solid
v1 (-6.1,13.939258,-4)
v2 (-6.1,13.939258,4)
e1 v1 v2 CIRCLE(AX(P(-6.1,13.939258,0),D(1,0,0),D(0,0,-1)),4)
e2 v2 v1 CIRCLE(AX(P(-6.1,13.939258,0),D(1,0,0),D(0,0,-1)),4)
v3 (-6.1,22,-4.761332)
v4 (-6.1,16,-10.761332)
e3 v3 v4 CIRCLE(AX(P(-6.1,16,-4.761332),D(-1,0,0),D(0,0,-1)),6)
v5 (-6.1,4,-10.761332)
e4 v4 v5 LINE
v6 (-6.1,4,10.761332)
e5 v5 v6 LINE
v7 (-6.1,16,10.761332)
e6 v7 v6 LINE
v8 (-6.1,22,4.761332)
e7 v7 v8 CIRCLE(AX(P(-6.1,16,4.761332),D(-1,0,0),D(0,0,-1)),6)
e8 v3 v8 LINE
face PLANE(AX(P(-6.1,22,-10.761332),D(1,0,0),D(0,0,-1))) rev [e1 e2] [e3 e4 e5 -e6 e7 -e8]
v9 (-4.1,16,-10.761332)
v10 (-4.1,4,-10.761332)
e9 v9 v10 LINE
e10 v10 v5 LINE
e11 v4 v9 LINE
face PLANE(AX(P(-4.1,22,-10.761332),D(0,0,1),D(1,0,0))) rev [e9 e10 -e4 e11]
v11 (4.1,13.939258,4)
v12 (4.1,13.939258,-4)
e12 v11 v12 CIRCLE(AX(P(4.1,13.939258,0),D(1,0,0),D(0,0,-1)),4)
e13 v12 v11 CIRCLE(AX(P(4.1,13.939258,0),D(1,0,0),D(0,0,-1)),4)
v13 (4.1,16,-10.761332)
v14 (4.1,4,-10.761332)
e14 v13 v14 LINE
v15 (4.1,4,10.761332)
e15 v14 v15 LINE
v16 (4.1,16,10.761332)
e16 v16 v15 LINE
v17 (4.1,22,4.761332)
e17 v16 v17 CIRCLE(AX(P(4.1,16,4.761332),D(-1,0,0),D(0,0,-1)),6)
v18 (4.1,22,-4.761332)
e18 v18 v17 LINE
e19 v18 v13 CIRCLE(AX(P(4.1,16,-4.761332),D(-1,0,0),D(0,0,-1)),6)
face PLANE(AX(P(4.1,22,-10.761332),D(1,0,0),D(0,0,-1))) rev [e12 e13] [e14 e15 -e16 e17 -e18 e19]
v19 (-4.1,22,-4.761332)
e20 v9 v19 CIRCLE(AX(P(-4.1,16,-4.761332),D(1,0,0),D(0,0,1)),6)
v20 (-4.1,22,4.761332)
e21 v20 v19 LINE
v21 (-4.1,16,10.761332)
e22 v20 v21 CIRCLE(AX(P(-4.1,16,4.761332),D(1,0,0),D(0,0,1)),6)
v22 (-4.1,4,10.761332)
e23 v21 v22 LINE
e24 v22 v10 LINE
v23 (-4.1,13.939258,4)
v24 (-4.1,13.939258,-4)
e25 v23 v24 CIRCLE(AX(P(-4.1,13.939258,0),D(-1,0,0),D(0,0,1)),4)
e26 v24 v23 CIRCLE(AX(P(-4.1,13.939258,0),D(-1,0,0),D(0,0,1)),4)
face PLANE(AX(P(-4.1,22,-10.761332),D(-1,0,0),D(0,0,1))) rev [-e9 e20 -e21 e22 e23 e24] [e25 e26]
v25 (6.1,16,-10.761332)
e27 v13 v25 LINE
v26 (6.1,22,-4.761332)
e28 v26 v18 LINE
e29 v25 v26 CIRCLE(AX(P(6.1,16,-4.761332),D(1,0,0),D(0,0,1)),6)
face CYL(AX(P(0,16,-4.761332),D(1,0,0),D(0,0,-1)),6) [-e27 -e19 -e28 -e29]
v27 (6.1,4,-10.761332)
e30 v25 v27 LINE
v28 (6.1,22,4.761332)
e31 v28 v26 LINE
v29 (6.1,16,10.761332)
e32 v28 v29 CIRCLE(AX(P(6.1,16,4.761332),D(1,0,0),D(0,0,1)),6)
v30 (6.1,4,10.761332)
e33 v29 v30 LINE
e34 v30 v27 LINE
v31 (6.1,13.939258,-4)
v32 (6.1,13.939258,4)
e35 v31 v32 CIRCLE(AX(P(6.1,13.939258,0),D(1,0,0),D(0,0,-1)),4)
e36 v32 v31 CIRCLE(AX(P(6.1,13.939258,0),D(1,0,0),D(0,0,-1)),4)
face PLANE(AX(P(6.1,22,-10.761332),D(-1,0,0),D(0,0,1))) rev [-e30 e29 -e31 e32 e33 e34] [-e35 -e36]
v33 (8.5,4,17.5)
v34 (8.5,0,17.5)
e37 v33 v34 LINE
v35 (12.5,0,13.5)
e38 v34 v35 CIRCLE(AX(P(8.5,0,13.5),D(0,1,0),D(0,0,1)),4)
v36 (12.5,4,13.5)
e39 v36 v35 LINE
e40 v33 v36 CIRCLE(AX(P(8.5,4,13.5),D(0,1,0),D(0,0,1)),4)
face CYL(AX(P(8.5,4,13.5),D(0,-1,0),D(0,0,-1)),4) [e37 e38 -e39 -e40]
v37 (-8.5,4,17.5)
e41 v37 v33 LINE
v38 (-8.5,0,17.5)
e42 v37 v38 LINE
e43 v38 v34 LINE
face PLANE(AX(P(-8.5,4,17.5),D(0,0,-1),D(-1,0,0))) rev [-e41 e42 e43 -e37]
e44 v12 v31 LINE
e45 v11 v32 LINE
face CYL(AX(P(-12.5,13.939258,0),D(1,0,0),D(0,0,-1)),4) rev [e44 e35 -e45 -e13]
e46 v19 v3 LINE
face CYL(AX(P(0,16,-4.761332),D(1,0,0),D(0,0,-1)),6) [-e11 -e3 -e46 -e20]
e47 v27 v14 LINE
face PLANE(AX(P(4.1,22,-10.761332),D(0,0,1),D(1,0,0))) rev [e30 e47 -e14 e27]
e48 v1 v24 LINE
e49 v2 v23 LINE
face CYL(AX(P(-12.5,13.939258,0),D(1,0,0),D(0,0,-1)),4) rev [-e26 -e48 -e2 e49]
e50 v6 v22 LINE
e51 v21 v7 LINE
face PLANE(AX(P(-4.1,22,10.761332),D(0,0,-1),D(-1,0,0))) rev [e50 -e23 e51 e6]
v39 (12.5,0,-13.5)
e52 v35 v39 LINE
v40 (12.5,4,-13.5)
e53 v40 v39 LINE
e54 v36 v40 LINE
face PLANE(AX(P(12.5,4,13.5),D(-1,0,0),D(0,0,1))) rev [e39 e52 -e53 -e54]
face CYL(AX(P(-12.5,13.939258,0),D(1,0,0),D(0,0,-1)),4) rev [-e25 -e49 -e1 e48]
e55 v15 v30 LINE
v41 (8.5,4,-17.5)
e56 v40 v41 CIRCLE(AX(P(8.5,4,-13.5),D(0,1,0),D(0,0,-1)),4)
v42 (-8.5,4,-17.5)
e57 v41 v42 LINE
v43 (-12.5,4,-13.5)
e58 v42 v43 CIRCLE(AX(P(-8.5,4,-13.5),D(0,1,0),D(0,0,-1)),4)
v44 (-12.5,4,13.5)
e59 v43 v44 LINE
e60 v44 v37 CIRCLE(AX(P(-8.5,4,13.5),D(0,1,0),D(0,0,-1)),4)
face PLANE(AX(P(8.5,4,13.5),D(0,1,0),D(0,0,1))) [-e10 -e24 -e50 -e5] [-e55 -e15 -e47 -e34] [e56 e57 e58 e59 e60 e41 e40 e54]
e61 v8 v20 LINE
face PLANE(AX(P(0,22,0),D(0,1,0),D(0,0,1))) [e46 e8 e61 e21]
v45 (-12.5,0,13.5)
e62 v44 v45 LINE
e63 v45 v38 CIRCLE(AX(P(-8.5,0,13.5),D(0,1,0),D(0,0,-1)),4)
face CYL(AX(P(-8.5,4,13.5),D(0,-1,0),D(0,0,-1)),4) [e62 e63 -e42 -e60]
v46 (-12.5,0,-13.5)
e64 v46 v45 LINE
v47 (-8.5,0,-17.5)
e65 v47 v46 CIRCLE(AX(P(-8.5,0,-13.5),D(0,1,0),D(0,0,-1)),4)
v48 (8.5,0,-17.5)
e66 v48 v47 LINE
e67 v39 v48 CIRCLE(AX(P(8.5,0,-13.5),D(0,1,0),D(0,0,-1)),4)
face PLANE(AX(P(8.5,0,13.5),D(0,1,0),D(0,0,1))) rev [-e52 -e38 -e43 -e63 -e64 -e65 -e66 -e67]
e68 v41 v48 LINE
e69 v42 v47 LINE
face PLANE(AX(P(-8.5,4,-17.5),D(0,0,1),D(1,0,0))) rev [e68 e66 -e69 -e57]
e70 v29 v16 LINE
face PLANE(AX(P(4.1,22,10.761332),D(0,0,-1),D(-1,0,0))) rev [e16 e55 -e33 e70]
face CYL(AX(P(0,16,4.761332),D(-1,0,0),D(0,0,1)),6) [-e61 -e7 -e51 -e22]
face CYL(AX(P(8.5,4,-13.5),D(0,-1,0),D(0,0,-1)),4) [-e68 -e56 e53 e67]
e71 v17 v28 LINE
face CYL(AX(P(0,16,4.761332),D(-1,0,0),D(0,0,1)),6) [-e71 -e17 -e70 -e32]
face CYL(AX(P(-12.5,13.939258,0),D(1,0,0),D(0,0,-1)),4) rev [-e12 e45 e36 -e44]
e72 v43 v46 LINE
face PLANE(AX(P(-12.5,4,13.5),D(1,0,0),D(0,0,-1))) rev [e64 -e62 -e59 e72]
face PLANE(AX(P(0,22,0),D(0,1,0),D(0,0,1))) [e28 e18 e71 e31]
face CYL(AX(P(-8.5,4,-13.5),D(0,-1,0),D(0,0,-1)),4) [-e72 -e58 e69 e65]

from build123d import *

# Parameters (mm, degrees)
BOSS_EXTRU_1_DEPTH = 4
SKETCH2_W          = 2
SKETCH2_H          = 21.522663516
BOSS_EXTRU_2_DEPTH = 18
FILLET1_R          = 6
SKETCH3_R          = 4
CUT_EXTRUDE1_DEPTH = 34.707714251


with BuildPart() as part:
    # Sketch1 → Boss.-Extru.1 (new body)
    with BuildSketch(Plane(origin=(0, 0, 0), x_dir=(1, 0, 0), z_dir=(0, 1, 0))):
        with BuildLine():
            Line((-8.5, -17.5), (8.5, -17.5))
            ThreePointArc((8.5, -17.5), (11.328427125, -16.328427125), (12.5, -13.5))
            Line((12.5, -13.5), (12.5, 13.5))
            ThreePointArc((12.5, 13.5), (11.328427125, 16.328427125), (8.5, 17.5))
            Line((8.5, 17.5), (-8.5, 17.5))
            ThreePointArc((-8.5, 17.5), (-11.328427125, 16.328427125), (-12.5, 13.5))
            Line((-12.5, 13.5), (-12.5, -13.5))
            ThreePointArc((-12.5, -13.5), (-11.328427125, -16.328427125), (-8.5, -17.5))
        make_face()
    extrude(amount=BOSS_EXTRU_1_DEPTH)

    # Sketch2 → Boss.-Extru.2 (add)
    with BuildSketch(Plane(origin=(0, 4, 0), x_dir=(1, 0, 0), z_dir=(0, 1, 0))):
        with Locations((-5.1, 0)):
            Rectangle(SKETCH2_W, SKETCH2_H)
        with Locations((5.1, 0)):
            Rectangle(SKETCH2_W, SKETCH2_H)
    extrude(amount=BOSS_EXTRU_2_DEPTH)

    # Fillet1
    fillet1_edges = [part.edges().sort_by_distance(p)[0] for p in [
        (5.1, 22, -10.761331758),
        (5.1, 22, 10.761331758),
        (-5.1, 22, -10.761331758),
        (-5.1, 22, 10.761331758),
    ]]
    fillet(fillet1_edges, radius=FILLET1_R)

    # Sketch3 → Cut-Extrude1 (cut, through all)
    with BuildSketch(Plane(origin=(6.1, 0, 0), x_dir=(0, 0, -1), z_dir=(1, 0, 0))):
        with Locations((0, 13.939258033)):
            Circle(SKETCH3_R)
    extrude(amount=-CUT_EXTRUDE1_DEPTH, mode=Mode.SUBTRACT)


solid = part.part
